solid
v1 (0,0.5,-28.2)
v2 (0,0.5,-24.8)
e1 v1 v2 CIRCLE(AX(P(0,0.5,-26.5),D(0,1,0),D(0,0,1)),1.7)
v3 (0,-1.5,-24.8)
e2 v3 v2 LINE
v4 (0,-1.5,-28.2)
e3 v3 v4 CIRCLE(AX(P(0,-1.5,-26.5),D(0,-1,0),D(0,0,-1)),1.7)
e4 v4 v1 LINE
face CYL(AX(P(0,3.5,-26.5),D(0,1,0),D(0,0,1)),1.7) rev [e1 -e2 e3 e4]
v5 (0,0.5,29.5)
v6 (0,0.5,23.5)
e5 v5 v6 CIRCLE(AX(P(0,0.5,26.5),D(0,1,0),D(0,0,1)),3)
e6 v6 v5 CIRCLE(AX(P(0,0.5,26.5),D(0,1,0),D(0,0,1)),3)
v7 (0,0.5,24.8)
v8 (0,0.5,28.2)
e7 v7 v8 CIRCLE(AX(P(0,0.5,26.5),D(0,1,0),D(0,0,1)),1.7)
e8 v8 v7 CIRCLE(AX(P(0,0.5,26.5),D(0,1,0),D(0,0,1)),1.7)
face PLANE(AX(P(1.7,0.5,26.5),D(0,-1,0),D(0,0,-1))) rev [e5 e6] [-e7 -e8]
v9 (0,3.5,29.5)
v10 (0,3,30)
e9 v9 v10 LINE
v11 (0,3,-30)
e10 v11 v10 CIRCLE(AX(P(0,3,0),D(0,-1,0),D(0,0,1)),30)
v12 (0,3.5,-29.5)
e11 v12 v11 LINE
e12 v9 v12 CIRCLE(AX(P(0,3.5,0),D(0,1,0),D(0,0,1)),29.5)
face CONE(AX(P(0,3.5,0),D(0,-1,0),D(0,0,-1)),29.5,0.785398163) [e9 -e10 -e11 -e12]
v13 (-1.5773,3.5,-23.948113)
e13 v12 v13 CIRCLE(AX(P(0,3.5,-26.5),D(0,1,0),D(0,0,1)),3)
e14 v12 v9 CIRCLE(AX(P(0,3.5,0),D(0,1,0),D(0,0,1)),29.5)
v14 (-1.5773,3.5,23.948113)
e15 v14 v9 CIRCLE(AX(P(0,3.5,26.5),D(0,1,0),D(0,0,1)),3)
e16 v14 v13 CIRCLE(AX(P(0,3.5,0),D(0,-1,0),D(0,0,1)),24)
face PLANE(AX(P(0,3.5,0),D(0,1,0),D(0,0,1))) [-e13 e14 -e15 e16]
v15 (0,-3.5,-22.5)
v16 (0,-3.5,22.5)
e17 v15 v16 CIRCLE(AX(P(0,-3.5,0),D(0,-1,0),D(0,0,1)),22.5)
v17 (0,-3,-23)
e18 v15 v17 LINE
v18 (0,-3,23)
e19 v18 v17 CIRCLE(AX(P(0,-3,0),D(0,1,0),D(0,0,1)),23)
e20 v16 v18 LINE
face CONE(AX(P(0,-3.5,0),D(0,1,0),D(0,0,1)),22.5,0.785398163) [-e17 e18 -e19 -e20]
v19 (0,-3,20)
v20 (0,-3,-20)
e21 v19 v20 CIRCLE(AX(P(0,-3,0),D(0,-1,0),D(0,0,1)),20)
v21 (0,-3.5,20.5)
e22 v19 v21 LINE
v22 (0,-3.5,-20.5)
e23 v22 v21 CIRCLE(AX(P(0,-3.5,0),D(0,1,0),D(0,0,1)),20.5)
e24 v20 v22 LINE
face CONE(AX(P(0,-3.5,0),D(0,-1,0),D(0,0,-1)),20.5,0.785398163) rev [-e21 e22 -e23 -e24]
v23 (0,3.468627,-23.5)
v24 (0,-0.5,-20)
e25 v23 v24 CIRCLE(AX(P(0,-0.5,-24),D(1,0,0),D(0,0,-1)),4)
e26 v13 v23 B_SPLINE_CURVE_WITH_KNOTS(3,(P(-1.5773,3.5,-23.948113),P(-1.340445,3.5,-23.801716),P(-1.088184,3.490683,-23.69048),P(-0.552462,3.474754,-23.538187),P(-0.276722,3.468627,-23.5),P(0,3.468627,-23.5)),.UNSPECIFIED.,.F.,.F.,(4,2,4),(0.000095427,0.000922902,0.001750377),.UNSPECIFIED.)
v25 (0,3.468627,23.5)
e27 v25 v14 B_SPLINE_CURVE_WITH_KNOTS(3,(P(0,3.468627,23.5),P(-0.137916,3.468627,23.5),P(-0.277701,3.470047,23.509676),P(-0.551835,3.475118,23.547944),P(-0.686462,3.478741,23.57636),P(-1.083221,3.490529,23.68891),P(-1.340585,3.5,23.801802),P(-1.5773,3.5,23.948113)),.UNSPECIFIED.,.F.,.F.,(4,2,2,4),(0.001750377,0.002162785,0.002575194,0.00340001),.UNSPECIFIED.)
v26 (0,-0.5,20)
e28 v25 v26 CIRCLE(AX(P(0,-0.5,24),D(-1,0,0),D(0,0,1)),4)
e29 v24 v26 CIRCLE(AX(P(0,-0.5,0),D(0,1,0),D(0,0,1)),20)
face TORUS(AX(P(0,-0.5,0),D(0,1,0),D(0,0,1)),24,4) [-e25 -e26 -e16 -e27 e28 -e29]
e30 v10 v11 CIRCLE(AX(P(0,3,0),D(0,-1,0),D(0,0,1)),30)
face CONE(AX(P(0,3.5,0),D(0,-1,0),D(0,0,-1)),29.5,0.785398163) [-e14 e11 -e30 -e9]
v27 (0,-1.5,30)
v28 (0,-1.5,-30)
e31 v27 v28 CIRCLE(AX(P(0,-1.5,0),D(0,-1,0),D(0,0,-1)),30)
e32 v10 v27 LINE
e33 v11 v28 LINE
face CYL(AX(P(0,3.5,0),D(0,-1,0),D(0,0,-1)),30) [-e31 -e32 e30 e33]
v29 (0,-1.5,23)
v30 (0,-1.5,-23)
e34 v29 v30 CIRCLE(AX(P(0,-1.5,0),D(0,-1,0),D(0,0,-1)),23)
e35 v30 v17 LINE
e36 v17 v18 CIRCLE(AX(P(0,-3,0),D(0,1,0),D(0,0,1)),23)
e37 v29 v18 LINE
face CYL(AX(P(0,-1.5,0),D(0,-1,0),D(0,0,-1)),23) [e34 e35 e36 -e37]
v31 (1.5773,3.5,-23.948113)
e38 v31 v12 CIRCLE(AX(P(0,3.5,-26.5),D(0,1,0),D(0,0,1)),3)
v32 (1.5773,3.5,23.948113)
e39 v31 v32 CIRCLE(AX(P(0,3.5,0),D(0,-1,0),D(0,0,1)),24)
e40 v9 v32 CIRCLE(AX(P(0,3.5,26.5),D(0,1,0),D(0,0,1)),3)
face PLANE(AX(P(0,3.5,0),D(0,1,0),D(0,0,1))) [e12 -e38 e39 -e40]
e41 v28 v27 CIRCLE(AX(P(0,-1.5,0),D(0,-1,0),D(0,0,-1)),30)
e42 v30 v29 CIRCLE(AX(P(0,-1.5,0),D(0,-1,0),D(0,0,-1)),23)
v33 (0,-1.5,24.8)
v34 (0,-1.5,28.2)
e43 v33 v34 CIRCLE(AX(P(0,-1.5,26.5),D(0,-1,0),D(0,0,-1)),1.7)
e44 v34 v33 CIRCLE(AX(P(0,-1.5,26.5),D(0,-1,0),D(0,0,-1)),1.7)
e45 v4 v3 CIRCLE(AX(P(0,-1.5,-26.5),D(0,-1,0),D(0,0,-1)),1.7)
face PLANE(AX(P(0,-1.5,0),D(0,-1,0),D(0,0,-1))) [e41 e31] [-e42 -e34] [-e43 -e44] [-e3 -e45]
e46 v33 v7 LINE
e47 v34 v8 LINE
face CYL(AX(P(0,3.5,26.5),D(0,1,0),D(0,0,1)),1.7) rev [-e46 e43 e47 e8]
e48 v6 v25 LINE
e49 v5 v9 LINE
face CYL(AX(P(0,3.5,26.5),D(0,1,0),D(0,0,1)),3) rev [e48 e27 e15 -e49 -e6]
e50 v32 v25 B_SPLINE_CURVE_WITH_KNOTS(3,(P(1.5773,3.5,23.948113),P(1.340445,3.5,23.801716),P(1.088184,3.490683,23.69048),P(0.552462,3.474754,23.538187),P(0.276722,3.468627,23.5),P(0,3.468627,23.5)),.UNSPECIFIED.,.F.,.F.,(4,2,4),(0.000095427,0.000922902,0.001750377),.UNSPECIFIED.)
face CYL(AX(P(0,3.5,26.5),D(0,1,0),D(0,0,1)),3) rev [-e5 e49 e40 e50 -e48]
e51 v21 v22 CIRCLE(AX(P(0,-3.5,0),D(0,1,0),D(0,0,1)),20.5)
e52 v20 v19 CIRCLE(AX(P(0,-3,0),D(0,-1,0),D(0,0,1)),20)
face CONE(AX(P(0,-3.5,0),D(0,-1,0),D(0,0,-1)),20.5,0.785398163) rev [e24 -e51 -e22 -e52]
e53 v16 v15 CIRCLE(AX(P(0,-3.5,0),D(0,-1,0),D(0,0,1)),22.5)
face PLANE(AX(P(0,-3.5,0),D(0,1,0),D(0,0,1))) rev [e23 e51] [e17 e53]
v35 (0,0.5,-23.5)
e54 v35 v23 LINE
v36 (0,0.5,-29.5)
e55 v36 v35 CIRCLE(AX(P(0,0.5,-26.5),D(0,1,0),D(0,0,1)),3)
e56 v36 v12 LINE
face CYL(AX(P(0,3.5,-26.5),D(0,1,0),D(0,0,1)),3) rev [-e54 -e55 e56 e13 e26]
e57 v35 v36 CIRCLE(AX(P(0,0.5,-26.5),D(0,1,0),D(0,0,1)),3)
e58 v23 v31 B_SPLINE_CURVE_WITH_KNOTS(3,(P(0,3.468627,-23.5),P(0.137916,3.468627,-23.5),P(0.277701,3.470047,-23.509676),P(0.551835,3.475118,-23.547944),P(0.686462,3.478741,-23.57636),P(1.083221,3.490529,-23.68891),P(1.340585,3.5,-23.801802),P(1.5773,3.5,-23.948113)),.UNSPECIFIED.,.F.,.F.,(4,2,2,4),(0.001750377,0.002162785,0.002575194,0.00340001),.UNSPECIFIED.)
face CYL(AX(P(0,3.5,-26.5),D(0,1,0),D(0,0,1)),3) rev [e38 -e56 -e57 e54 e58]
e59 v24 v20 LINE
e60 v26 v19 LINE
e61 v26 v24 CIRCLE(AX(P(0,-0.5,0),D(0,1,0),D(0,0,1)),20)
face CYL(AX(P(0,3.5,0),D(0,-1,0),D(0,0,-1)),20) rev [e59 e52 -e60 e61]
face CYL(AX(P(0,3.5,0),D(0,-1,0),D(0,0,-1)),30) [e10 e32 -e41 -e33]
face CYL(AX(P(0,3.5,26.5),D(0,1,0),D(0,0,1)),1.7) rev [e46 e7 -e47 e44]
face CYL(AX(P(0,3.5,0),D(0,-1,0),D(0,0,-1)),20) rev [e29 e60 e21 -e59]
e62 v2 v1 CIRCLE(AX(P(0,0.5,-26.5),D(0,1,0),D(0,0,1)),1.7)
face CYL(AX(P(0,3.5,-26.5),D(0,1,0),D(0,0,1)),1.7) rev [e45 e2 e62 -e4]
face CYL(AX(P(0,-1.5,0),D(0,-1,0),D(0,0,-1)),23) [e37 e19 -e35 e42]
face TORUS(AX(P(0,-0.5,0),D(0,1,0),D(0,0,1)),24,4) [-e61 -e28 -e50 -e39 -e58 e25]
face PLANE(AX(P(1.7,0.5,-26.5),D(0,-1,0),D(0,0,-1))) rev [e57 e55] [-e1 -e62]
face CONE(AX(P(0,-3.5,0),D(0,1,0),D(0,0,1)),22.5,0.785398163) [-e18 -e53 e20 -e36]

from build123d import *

# Parameters (mm, degrees)
SKETCH1_R                                            = 30
SKETCH1_R_2                                          = 20
BOSS_EXTRUDE1_DEPTH                                  = 3.5
SKETCH2_OUTSIDE_W                                    = 79.028
SKETCH2_OUTSIDE_H                                    = 79.028
SKETCH2_OUTSIDE_R                                    = 23
CUT_EXTRUDE1_DEPTH                                   = 2
FILLET1_R                                            = 4
CHAMFER1_SIZE                                        = 0.5
HOLE_SIZE_BY_SOCKET_HEAD_CAP_SCREW_TYPE1_D           = 3.4
HOLE_SIZE_BY_SOCKET_HEAD_CAP_SCREW_TYPE1_CBORE_D     = 6
HOLE_SIZE_BY_SOCKET_HEAD_CAP_SCREW_TYPE1_CBORE_DEPTH = 3


with BuildPart() as part:
    # Sketch1 → Boss-Extrude1 (new, symmetric)
    with BuildSketch(Plane(origin=(0, 0, 0), x_dir=(1, 0, 0), z_dir=(0, 1, 0))):
        with Locations(Location((0, 0, 0), (0, 0, 270))):
            Circle(SKETCH1_R)
        with Locations(Location((0, 0, 0), (0, 0, 270))):
            Circle(SKETCH1_R_2, mode=Mode.SUBTRACT)
    extrude(amount=BOSS_EXTRUDE1_DEPTH, both=True)

    # Sketch2 outside → Cut-Extrude1 (cut)
    with BuildSketch(Plane.XZ.offset(3.5)):
        Rectangle(SKETCH2_OUTSIDE_W, SKETCH2_OUTSIDE_H)
        with Locations(Location((0, 0, 0), (0, 0, 270))):
            Circle(SKETCH2_OUTSIDE_R, mode=Mode.SUBTRACT)
    extrude(amount=-CUT_EXTRUDE1_DEPTH, mode=Mode.SUBTRACT)

    # Fillet1
    fillet1_edges = [part.edges().sort_by_distance(p)[0] for p in [
        (0, 3.5, -20),
    ]]
    fillet(fillet1_edges, radius=FILLET1_R)

    # Chamfer1
    chamfer1_edges = [part.edges().sort_by_distance(p)[0] for p in [
        (0, -3.5, 23),
        (0, 3.5, -30),
        (0, -3.5, -20),
    ]]
    chamfer(chamfer1_edges, length=CHAMFER1_SIZE)

    # Hole Size by Socket Head Cap Screw Type1 (through all)
    with Locations(Plane(origin=(0, 3.5, 0), x_dir=(1, 0, 0), z_dir=(0, 1, 0))):
        with Locations((0, -26.5), (0, 26.5)):
            CounterBoreHole(HOLE_SIZE_BY_SOCKET_HEAD_CAP_SCREW_TYPE1_D / 2, HOLE_SIZE_BY_SOCKET_HEAD_CAP_SCREW_TYPE1_CBORE_D / 2, HOLE_SIZE_BY_SOCKET_HEAD_CAP_SCREW_TYPE1_CBORE_DEPTH)


solid = part.part
